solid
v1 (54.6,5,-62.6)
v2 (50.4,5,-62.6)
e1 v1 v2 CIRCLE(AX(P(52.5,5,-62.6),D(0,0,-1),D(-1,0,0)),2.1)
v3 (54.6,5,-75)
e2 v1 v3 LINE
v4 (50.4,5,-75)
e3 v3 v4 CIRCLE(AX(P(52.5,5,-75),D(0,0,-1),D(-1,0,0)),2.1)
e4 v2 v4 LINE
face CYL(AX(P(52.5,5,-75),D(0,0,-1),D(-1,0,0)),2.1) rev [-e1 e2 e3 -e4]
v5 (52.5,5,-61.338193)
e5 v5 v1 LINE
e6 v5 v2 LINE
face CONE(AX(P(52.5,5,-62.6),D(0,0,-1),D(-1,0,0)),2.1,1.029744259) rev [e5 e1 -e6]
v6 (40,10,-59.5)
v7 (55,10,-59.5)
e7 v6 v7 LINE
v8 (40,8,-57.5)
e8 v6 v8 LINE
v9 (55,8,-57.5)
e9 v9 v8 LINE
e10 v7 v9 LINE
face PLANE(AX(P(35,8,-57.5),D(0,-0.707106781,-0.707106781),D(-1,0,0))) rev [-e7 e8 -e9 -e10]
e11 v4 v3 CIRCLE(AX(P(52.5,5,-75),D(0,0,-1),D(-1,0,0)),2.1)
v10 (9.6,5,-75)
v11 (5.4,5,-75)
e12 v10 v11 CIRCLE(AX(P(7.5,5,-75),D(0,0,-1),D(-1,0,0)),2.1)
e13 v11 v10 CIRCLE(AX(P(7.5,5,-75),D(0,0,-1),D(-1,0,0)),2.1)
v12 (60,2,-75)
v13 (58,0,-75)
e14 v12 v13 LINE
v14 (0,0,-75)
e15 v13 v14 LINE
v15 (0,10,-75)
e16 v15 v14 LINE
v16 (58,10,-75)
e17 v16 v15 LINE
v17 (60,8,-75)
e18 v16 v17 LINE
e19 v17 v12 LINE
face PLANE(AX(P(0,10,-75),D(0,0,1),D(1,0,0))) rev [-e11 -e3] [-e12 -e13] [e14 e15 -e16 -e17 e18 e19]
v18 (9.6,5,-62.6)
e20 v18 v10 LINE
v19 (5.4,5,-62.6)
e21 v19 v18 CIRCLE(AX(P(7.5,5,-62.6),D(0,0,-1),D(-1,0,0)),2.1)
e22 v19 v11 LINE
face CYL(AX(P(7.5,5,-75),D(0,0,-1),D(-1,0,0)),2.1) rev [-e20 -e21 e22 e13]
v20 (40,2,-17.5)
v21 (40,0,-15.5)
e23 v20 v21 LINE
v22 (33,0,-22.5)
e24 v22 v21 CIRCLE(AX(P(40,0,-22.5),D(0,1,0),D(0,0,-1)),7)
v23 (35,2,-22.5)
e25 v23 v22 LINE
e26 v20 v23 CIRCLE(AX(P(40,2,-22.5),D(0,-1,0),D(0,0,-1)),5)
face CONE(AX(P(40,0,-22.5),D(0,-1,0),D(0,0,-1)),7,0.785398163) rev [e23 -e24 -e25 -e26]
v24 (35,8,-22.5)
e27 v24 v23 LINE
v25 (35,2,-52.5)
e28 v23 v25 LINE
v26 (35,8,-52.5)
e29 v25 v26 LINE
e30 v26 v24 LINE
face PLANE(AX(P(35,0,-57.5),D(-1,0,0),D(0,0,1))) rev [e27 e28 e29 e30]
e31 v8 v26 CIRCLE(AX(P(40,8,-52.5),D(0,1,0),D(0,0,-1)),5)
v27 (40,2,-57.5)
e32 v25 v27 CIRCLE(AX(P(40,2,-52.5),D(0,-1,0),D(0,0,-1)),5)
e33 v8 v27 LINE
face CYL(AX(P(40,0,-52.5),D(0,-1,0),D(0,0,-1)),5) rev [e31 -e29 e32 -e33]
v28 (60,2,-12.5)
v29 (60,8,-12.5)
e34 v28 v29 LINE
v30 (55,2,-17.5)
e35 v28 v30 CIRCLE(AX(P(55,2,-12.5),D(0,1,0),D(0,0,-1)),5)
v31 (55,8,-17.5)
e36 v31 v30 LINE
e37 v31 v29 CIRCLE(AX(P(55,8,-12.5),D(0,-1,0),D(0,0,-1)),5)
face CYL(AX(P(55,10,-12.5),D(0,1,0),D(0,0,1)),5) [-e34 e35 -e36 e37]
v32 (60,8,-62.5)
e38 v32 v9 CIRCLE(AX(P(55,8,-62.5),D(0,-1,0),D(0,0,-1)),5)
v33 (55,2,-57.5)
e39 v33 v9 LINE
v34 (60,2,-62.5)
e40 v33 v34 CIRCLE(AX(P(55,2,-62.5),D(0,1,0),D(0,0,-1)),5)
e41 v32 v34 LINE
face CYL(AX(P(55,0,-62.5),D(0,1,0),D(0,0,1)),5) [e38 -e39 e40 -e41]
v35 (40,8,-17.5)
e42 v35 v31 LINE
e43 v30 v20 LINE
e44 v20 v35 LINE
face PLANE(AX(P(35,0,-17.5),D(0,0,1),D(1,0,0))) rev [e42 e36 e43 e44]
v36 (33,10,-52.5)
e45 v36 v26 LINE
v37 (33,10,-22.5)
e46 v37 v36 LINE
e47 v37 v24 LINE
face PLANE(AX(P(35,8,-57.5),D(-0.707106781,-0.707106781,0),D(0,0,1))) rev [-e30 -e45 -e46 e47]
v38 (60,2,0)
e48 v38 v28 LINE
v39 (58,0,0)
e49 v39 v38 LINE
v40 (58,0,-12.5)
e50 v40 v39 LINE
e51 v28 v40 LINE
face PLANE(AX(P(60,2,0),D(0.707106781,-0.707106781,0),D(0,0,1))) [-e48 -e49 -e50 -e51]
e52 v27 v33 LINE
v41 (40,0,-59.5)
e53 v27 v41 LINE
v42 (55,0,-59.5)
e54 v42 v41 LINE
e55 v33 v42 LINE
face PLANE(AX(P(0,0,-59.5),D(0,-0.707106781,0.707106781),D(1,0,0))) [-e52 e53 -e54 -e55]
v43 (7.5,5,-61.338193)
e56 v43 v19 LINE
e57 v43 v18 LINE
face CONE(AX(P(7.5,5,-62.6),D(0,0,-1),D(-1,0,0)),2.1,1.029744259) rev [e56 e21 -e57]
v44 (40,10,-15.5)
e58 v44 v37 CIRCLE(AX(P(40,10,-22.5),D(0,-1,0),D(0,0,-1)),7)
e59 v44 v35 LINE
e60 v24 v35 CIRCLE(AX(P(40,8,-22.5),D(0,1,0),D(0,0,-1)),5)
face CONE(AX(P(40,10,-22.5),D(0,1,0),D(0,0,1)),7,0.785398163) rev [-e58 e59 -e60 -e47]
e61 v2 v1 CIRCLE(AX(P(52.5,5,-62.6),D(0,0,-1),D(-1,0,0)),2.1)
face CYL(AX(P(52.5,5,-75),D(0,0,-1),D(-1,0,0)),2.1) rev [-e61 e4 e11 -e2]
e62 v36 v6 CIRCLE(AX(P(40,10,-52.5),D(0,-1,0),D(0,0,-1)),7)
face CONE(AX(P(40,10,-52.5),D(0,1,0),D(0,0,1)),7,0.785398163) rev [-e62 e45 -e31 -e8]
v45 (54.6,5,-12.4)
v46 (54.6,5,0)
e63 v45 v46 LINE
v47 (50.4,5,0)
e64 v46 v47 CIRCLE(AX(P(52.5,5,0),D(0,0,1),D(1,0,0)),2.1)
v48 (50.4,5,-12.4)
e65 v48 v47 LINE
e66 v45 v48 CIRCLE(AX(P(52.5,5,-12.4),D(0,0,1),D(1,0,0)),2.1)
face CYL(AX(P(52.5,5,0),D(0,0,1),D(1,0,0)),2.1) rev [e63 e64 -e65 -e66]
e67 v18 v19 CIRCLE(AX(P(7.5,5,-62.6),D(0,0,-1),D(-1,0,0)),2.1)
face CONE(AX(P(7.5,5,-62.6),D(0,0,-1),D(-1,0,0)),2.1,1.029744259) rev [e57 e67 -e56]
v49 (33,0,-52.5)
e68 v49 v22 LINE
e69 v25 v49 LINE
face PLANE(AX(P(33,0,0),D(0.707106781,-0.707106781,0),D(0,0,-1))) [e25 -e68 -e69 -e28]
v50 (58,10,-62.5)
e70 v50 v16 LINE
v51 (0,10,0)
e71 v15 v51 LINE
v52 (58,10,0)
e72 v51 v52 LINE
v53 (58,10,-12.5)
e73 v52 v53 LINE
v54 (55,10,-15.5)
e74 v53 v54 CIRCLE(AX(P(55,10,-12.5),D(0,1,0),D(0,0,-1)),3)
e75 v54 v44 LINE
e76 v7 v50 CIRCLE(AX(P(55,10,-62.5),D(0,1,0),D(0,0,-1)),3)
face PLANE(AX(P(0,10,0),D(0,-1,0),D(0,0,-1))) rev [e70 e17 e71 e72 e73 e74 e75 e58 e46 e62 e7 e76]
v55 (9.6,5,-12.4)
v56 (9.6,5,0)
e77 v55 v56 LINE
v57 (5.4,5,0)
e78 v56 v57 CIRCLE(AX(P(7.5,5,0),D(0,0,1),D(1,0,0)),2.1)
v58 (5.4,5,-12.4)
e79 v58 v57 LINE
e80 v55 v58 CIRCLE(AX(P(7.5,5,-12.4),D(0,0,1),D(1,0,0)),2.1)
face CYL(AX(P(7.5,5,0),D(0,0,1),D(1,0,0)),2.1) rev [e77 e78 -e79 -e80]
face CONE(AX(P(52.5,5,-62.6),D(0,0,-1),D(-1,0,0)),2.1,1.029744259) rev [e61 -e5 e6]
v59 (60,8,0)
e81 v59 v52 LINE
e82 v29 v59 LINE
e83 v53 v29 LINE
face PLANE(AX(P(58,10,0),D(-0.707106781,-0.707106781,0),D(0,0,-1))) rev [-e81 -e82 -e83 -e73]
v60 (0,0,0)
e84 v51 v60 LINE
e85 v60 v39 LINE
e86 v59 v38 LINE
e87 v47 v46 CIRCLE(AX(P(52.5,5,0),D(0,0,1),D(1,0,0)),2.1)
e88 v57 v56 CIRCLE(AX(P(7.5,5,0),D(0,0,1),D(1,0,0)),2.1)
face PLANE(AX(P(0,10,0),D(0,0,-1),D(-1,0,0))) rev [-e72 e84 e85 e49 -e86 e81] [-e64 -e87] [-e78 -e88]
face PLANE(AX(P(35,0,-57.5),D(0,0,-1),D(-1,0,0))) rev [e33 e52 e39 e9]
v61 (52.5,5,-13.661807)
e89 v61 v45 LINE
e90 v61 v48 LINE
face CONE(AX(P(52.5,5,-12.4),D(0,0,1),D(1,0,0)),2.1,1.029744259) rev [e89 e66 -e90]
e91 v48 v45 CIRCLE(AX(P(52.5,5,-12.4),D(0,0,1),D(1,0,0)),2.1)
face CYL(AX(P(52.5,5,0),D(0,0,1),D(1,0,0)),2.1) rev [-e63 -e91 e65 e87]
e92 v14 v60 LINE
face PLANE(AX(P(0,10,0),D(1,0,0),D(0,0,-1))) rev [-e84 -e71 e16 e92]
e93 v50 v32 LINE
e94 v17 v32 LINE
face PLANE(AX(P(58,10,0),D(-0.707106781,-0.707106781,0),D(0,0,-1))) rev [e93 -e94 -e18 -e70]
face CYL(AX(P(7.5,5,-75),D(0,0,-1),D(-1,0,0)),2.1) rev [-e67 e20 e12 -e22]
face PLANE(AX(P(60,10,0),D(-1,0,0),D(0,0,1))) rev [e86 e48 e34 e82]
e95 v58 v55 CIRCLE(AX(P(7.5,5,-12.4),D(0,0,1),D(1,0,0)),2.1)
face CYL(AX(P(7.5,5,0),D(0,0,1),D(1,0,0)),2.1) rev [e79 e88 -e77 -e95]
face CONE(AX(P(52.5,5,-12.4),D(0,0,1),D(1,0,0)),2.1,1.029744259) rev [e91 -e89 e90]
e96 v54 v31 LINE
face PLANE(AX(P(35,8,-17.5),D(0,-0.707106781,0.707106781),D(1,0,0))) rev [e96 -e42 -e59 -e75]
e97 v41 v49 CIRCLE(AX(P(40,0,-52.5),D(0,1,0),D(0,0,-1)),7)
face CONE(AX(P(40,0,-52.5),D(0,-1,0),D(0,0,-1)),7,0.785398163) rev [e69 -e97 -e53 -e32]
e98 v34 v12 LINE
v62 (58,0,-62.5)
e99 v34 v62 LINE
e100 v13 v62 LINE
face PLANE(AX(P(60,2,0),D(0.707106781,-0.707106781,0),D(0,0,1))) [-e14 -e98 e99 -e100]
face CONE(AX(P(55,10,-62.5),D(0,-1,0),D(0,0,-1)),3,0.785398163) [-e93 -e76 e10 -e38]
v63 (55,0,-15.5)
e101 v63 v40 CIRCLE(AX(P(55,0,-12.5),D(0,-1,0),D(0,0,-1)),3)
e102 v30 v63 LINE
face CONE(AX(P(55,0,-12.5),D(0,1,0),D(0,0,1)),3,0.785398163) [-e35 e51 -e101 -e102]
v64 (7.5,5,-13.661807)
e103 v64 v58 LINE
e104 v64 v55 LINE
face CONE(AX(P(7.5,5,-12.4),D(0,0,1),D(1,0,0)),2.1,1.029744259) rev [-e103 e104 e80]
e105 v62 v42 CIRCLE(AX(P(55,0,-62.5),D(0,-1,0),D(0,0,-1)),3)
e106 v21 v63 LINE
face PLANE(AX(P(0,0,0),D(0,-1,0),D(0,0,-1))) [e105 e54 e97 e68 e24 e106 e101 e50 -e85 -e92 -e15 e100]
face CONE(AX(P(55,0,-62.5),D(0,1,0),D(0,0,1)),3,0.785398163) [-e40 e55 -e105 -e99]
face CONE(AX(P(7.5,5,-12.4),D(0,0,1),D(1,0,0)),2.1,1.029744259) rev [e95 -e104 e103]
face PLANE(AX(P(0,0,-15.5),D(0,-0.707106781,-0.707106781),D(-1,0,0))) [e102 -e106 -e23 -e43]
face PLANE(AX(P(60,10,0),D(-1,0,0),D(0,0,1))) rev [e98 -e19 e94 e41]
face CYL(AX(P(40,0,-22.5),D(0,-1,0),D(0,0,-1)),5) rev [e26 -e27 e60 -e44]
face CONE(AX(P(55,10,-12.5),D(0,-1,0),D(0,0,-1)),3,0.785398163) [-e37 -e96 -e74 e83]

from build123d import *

# Parameters (mm, degrees)
SKETCH1_W             = 60
SKETCH1_H             = 75
BOSS_EXTRUDE1_DEPTH   = 10
M5_TAPPED_HOLE1_D     = 4.2
M5_TAPPED_HOLE1_DEPTH = 12.4
M5_TAPPED_HOLE1_TIP   = 1.2618073
M5_TAPPED_HOLE2_D     = 4.2
M5_TAPPED_HOLE2_DEPTH = 12.4
M5_TAPPED_HOLE2_TIP   = 1.2618073
SKETCH9_W             = 25
SKETCH9_H             = 40
CUT_EXTRUDE1_DEPTH    = 97.566039579
FILLET1_R             = 5
CHAMFER1_SIZE         = 2


with BuildPart() as part:
    # Sketch1 → Boss-Extrude1 (new body)
    with BuildSketch(Plane(origin=(0, 0, 0), x_dir=(1, 0, 0), z_dir=(0, 1, 0))):
        with Locations((30, 37.5)):
            Rectangle(SKETCH1_W, SKETCH1_H)
    extrude(amount=BOSS_EXTRUDE1_DEPTH)

    # M5 Tapped Hole1
    with Locations(Plane(origin=(0, 0, -75), x_dir=(-1, 0, 0), z_dir=(0, 0, -1))):
        with Locations((-7.5, 5), (-52.5, 5)):
            Hole(M5_TAPPED_HOLE1_D / 2, depth=M5_TAPPED_HOLE1_DEPTH)
            with Locations((0, 0, -(M5_TAPPED_HOLE1_DEPTH + M5_TAPPED_HOLE1_TIP / 2))):  # 118° drill point
                Cone(0, M5_TAPPED_HOLE1_D / 2, M5_TAPPED_HOLE1_TIP, mode=Mode.SUBTRACT)

    # M5 Tapped Hole2
    with Locations(Plane.XY):
        with Locations((52.5, 5), (7.5, 5)):
            Hole(M5_TAPPED_HOLE2_D / 2, depth=M5_TAPPED_HOLE2_DEPTH)
            with Locations((0, 0, -(M5_TAPPED_HOLE2_DEPTH + M5_TAPPED_HOLE2_TIP / 2))):  # 118° drill point
                Cone(0, M5_TAPPED_HOLE2_D / 2, M5_TAPPED_HOLE2_TIP, mode=Mode.SUBTRACT)

    # Sketch9 → Cut-Extrude1 (cut, through all)
    with BuildSketch(Plane(origin=(0, 10, 0), x_dir=(1, 0, 0), z_dir=(0, 1, 0))):
        with Locations((47.5, 37.5)):
            Rectangle(SKETCH9_W, SKETCH9_H)
    extrude(amount=-CUT_EXTRUDE1_DEPTH, mode=Mode.SUBTRACT)

    # Fillet1
    fillet1_edges = [part.edges().sort_by_distance(p)[0] for p in [
        (35, 5, -17.5),
        (35, 5, -57.5),
        (60, 5, -57.5),
        (60, 5, -17.5),
    ]]
    fillet(fillet1_edges, radius=FILLET1_R)

    # Chamfer1
    chamfer1_edges = [part.edges().sort_by_distance(p)[0] for p in [
        (60, 10, -6.25),
        (47.5, 10, -57.5),
        (47.5, 0, -57.5),
        (35, 10, -37.5),
        (60, 10, -68.75),
        (60, 0, -6.25),
        (47.5, 10, -17.5),
        (58.535533906, 10, -16.035533906),
        (58.535533906, 10, -58.964466094),
        (60, 0, -68.75),
        (35, 0, -37.5),
        (47.5, 0, -17.5),
        (58.535533906, 0, -16.035533906),
        (58.535533906, 0, -58.964466094),
        (36.464466094, 10, -18.964466094),
        (36.464466094, 0, -18.964466094),
        (36.464466094, 10, -56.035533906),
        (36.464466094, 0, -56.035533906),
    ]]
    chamfer(chamfer1_edges, length=CHAMFER1_SIZE)


solid = part.part
